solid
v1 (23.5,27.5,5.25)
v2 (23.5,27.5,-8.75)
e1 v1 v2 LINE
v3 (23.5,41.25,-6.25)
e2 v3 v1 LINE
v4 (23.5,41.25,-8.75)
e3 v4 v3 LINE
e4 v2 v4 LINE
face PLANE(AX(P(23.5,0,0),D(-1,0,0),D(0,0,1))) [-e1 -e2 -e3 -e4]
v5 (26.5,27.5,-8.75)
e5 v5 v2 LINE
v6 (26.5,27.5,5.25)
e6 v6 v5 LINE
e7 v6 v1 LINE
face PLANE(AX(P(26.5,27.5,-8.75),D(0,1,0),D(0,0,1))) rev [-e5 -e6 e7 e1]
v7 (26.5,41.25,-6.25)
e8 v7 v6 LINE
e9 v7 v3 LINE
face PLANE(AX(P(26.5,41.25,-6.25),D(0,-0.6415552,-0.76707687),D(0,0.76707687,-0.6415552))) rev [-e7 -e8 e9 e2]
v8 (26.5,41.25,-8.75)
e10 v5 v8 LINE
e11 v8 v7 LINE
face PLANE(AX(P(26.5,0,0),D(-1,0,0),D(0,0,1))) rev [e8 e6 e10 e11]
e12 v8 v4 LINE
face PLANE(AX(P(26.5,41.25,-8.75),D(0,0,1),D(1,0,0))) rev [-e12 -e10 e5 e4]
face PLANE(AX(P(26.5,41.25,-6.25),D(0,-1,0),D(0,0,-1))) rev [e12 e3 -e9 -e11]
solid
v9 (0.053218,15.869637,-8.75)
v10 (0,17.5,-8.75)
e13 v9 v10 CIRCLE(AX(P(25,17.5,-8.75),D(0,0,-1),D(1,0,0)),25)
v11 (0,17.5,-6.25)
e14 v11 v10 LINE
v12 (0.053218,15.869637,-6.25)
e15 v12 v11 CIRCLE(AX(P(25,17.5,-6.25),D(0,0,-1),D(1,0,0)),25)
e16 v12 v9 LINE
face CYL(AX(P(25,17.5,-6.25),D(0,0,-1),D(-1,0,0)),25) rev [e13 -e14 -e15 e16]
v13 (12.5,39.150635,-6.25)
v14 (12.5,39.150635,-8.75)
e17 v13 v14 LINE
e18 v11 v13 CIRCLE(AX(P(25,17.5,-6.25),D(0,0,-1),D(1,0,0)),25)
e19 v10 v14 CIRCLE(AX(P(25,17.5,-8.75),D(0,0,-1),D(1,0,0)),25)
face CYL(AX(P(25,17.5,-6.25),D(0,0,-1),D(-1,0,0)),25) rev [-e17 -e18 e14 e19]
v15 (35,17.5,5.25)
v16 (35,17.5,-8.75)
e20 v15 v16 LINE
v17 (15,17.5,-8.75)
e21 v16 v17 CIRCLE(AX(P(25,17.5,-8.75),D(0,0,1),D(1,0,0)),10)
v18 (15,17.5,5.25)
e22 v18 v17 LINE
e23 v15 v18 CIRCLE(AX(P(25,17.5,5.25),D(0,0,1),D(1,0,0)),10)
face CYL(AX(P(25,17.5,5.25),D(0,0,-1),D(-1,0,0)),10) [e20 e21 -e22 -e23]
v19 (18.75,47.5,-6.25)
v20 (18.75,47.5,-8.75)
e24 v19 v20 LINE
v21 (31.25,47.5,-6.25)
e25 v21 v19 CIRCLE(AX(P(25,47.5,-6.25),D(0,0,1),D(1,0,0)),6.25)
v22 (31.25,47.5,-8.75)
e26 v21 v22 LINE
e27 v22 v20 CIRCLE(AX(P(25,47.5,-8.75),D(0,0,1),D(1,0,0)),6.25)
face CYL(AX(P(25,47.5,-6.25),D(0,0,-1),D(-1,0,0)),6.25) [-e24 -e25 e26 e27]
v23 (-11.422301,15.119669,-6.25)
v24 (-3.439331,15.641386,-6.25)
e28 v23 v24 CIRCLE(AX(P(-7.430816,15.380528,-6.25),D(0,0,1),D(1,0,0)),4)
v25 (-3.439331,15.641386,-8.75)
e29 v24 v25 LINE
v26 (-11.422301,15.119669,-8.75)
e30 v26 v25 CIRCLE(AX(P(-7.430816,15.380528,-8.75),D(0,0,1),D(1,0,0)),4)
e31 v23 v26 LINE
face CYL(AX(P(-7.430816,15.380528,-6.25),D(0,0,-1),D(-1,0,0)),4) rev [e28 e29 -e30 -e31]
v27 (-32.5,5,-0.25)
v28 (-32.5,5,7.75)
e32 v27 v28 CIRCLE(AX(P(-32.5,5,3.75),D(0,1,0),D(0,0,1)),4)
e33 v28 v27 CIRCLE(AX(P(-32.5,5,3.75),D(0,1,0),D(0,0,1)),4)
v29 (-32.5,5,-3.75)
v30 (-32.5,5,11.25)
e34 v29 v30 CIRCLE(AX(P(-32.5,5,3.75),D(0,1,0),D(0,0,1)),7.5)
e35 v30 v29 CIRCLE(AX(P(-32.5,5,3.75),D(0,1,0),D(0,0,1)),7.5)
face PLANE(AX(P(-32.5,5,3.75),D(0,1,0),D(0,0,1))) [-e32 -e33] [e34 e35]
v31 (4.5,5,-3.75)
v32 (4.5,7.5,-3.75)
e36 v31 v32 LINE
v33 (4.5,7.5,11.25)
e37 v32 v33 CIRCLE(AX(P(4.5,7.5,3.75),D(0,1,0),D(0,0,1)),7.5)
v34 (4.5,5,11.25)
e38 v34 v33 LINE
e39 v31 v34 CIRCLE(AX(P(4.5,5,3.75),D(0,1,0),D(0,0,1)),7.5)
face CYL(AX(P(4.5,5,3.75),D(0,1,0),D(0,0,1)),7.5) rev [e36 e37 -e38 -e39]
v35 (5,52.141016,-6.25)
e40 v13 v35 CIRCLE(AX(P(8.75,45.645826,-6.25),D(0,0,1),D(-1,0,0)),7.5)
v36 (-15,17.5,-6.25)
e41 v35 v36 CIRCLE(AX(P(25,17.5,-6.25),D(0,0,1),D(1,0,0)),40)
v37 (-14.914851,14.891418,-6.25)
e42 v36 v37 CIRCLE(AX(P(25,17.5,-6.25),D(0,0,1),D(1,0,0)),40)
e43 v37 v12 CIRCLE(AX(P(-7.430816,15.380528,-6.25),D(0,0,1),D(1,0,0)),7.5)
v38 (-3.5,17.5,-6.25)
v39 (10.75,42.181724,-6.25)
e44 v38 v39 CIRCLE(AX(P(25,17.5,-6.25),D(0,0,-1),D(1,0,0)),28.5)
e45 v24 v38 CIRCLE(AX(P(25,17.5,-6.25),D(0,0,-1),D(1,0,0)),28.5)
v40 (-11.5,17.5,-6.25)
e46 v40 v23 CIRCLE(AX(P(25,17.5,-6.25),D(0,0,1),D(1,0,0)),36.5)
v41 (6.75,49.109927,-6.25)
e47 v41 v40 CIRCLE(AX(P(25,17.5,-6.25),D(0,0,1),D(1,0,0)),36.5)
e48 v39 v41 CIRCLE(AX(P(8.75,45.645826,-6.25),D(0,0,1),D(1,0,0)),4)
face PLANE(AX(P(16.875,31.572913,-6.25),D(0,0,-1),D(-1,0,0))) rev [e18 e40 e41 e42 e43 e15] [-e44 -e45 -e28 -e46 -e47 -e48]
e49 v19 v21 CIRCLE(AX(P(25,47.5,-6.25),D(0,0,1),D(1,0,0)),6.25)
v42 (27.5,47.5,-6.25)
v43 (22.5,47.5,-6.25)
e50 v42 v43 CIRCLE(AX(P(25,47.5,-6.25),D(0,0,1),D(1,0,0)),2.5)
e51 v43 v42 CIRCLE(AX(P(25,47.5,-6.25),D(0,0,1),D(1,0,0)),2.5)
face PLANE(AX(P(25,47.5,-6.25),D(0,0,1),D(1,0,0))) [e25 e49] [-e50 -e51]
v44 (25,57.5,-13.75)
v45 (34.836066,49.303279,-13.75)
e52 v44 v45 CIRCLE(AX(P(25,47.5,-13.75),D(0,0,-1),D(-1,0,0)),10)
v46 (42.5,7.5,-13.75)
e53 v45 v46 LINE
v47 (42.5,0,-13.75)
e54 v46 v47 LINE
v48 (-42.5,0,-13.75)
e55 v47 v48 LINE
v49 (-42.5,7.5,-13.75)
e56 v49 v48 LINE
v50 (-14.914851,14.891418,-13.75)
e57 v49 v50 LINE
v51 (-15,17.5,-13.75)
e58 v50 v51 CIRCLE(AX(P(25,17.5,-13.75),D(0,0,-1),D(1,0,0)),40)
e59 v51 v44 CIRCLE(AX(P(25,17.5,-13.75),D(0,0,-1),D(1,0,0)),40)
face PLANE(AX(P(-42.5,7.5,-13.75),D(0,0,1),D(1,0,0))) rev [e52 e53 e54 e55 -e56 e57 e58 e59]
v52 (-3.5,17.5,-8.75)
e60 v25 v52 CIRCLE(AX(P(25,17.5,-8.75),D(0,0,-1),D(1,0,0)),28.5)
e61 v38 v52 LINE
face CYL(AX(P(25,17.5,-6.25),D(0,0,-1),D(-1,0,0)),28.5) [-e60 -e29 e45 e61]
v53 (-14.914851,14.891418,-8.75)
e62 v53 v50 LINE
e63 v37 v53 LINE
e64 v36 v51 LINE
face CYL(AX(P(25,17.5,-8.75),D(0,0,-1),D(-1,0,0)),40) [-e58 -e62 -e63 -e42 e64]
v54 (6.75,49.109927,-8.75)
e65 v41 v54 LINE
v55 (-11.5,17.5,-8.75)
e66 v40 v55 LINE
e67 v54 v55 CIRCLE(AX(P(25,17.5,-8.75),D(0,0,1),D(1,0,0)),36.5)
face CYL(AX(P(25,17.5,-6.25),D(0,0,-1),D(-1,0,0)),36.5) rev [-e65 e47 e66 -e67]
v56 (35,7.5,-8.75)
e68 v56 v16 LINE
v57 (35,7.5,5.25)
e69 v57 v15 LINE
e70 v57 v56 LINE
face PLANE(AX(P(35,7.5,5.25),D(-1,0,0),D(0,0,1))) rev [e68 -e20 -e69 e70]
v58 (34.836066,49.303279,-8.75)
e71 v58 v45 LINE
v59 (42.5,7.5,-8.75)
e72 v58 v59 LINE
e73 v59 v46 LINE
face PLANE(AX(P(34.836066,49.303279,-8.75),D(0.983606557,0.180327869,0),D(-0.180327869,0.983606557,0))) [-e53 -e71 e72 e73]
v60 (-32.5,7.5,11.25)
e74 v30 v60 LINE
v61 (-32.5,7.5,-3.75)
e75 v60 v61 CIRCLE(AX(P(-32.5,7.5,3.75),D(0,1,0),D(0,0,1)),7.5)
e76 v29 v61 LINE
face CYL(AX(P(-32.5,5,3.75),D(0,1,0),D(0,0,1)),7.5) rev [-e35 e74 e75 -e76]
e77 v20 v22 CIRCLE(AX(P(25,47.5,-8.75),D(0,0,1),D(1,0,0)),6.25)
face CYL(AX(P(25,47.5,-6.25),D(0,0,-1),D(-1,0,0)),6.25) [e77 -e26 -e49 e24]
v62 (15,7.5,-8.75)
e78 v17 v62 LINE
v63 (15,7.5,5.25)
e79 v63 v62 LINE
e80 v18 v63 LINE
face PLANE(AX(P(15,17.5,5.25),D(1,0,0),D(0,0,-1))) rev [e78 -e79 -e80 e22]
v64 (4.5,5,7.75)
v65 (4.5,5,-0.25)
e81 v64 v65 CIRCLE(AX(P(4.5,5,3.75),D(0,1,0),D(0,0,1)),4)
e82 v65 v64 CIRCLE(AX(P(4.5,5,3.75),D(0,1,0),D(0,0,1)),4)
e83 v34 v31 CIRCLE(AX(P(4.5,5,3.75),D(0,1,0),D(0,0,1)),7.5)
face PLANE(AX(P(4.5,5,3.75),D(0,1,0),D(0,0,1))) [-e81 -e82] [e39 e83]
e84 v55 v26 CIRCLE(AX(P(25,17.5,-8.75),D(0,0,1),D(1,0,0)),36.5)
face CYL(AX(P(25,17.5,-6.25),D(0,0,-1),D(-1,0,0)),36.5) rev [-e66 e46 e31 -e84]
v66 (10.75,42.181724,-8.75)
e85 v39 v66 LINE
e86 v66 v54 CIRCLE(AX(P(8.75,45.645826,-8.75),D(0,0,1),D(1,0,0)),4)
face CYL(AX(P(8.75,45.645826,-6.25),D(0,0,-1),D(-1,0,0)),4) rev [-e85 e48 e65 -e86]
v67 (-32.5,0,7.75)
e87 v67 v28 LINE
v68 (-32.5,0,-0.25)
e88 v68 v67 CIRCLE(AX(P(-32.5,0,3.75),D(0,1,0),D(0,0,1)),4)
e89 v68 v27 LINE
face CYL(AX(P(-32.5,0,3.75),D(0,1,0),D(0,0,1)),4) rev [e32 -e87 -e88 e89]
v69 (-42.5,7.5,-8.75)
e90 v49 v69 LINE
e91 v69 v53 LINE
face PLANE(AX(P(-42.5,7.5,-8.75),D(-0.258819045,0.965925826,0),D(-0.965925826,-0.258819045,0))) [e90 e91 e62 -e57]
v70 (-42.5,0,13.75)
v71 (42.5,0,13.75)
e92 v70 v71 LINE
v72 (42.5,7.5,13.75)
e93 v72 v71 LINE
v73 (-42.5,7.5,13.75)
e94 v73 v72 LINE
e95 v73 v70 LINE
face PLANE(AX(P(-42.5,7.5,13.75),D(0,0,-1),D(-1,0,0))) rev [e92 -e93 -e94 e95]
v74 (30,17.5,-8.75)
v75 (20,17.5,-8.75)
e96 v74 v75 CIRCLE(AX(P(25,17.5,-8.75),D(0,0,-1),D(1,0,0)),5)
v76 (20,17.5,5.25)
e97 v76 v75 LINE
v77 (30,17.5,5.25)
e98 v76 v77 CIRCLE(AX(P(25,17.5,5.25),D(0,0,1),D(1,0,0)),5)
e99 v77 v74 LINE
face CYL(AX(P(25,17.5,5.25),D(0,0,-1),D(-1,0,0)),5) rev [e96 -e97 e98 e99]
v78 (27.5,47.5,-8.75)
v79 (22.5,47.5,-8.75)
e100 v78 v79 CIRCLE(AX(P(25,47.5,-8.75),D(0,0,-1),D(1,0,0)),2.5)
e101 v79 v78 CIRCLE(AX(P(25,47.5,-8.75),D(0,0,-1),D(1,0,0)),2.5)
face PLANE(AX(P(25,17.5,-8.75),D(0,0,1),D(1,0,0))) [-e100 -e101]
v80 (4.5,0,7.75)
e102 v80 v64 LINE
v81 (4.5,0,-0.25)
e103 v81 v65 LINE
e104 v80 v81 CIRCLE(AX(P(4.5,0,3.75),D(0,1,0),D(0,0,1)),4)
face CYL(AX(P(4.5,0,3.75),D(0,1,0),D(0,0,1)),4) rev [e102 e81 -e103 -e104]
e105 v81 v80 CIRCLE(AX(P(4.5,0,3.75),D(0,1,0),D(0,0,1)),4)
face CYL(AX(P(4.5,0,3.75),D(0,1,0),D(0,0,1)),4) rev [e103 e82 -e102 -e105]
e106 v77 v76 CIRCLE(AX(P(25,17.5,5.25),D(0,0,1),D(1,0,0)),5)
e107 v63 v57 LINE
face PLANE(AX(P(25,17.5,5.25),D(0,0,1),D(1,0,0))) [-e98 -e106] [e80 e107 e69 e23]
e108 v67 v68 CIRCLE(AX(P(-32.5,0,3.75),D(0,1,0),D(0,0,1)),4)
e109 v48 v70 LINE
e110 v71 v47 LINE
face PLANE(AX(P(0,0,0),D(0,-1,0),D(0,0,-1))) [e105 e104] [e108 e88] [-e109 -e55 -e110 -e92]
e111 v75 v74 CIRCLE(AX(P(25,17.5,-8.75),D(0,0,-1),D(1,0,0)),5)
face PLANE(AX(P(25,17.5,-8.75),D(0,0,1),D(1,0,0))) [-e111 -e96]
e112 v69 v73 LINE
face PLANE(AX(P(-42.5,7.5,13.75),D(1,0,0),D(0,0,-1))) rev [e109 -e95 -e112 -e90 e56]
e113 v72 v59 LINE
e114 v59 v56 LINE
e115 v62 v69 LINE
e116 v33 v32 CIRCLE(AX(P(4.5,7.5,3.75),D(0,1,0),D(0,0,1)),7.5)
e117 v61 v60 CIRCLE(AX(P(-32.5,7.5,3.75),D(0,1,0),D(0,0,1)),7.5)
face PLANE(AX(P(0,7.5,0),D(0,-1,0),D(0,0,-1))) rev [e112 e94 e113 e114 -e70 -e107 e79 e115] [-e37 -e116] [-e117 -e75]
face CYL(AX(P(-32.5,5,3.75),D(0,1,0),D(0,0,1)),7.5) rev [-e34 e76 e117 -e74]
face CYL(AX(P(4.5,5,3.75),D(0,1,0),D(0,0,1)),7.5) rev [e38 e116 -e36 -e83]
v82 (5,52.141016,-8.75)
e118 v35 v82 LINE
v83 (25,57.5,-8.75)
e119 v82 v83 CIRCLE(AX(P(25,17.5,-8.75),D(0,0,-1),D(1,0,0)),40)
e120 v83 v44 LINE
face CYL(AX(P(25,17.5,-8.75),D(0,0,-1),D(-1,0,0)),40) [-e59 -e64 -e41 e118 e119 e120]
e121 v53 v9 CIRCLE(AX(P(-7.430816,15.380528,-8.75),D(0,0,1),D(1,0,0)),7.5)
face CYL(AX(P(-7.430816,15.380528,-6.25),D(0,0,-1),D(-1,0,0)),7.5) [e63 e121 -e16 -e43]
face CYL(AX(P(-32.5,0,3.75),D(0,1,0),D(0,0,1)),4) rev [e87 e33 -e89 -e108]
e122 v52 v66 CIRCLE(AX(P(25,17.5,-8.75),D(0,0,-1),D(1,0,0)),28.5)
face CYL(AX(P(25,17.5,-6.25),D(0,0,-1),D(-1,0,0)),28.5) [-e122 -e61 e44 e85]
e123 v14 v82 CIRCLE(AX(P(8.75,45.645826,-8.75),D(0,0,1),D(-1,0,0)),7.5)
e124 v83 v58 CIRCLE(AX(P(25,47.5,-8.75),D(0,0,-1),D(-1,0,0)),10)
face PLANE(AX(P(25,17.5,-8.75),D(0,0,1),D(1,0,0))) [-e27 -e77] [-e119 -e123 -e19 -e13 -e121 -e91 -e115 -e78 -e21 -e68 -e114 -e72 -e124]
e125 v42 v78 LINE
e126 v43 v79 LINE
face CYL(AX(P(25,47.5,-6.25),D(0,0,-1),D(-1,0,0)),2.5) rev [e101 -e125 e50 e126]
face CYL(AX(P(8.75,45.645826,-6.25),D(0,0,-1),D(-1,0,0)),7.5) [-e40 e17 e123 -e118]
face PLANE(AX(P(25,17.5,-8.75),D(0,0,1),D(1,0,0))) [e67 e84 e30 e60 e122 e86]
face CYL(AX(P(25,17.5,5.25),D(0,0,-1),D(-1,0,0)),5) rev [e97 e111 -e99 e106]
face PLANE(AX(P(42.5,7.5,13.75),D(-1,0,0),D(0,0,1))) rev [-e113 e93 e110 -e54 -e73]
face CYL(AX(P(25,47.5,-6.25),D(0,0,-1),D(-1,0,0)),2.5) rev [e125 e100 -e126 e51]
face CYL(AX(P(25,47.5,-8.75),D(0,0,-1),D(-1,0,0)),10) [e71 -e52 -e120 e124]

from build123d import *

# Parameters (mm, degrees)
BASE_PLATE_SKETCH_W         = 85
BASE_PLATE_SKETCH_H         = 27.5
BASE_PLATE_DEPTH            = 7.5
UPRIGHT_DEPTH               = 5
UPRIGHT_RIM_BOSS_SKETCH_R   = 6.25
UPRIGHT_RIM_BOSS_SKETCH_R_2 = 2.5
UPRIGHT_RIM_BOSS_DEPTH      = 2.5
BUSHING_BLOCK_SKETCH_R      = 5
BUSHING_BLOCK_DEPTH         = 14
COUNTERBORE_SKETCH_2X_15_R  = 7.5
COUNTERBORES_2X_15_DEPTH    = 2.5
MOUNTING_HOLE_SKETCH_2X_8_R = 4
MOUNTING_HOLES_2X_8_DEPTH   = 69.931578395
LINK_PLATE_DEPTH            = 1.5
CURVED_GUIDE_RIB_DEPTH      = 2.5


with BuildPart() as part:
    # Base Plate Sketch → Base Plate (new body)
    with BuildSketch(Plane(origin=(0, 0, 0), x_dir=(1, 0, 0), z_dir=(0, 1, 0))):
        Rectangle(BASE_PLATE_SKETCH_W, BASE_PLATE_SKETCH_H)
    extrude(amount=BASE_PLATE_DEPTH)

    # Upright Profile Sketch → Upright (add)
    with BuildSketch(Plane(origin=(0, 0, -13.75), x_dir=(-1, 0, 0), z_dir=(0, 0, -1))):
        with BuildLine():
            Line((42.5, 7.5), (14.914850651, 14.891418491))
            ThreePointArc((14.914850651, 14.891418491), (4.191978867, 44.846450772), (-25, 57.5))
            ThreePointArc((-25, 57.5), (-31.401843997, 55.182212796), (-34.836065574, 49.303278689))
            Line((-34.836065574, 49.303278689), (-42.5, 7.5))
            Line((-42.5, 7.5), (42.5, 7.5))
        make_face()
    extrude(amount=-UPRIGHT_DEPTH)

    # Upright Rim Boss Sketch → Upright Rim Boss (add)
    with BuildSketch(Plane.XY.offset(-8.75)):
        with Locations((25, 47.5)):
            Circle(UPRIGHT_RIM_BOSS_SKETCH_R)
        with Locations((25, 47.5)):
            Circle(UPRIGHT_RIM_BOSS_SKETCH_R_2, mode=Mode.SUBTRACT)
    extrude(amount=UPRIGHT_RIM_BOSS_DEPTH)

    # Bushing Block Sketch → Bushing Block (add)
    with BuildSketch(Plane.XY.offset(-8.75)):
        with BuildLine():
            Line((15, 17.5), (15, 7.5))
            Line((15, 7.5), (35, 7.5))
            Line((35, 7.5), (35, 17.5))
            ThreePointArc((35, 17.5), (25, 27.5), (15, 17.5))
        make_face()
        with Locations((25, 17.5)):
            Circle(BUSHING_BLOCK_SKETCH_R, mode=Mode.SUBTRACT)
    extrude(amount=BUSHING_BLOCK_DEPTH)

    # Counterbore Sketch 2xØ15 → Counterbores 2xØ15 (cut)
    with BuildSketch(Plane(origin=(0, 7.5, 0), x_dir=(1, 0, 0), z_dir=(0, 1, 0))):
        with Locations(Location((4.5, -3.75, 0), (0, 0, 270))):
            Circle(COUNTERBORE_SKETCH_2X_15_R)
        with Locations(Location((-32.5, -3.75, 0), (0, 0, 270))):
            Circle(COUNTERBORE_SKETCH_2X_15_R)
    extrude(amount=-COUNTERBORES_2X_15_DEPTH, mode=Mode.SUBTRACT)

    # Mounting Hole Sketch 2xØ8 → Mounting Holes 2xØ8 (cut, through all)
    with BuildSketch(Plane(origin=(0, 5, 0), x_dir=(1, 0, 0), z_dir=(0, 1, 0))):
        with Locations(Location((-32.5, -3.75, 0), (0, 0, 270))):
            Circle(MOUNTING_HOLE_SKETCH_2X_8_R)
        with Locations(Location((4.5, -3.75, 0), (0, 0, 270))):
            Circle(MOUNTING_HOLE_SKETCH_2X_8_R)
    extrude(amount=-MOUNTING_HOLES_2X_8_DEPTH, mode=Mode.SUBTRACT)

    # Curved Guide Rib Sketch → Curved Guide Rib (add)
    with BuildSketch(Plane.XY.offset(-8.75)):
        with BuildLine():
            ThreePointArc((5, 52.141016151), (-10.275068584, 36.359202963), (-14.914850651, 14.891418491))
            ThreePointArc((-14.914850651, 14.891418491), (-6.941707121, 7.896493027), (0.053218343, 15.869636557))
            ThreePointArc((0.053218343, 15.869636557), (2.953082135, 29.287001852), (12.5, 39.150635095))
            ThreePointArc((12.5, 39.150635095), (15.245190528, 49.395825623), (5, 52.141016151))
        make_face()
        with BuildLine():
            ThreePointArc((6.75, 49.109927238), (-7.188500083, 34.709022704), (-11.422301219, 15.119669373))
            ThreePointArc((-11.422301219, 15.119669373), (-7.169958003, 11.389042459), (-3.439331089, 15.641385675))
            ThreePointArc((-3.439331089, 15.641385675), (-0.133486366, 30.937182111), (10.75, 42.181724008))
            ThreePointArc((10.75, 42.181724008), (12.214101615, 47.645825623), (6.75, 49.109927238))
        make_face(mode=Mode.SUBTRACT)
    extrude(amount=CURVED_GUIDE_RIB_DEPTH)


with BuildPart() as body_2:
    # Link Plate Sketch → Link Plate (new, symmetric)
    with BuildSketch(Plane(origin=(25, 0, 0), x_dir=(0, 0, -1), z_dir=(1, 0, 0))):
        Polygon((6.25, 41.25), (-5.25, 27.5), (8.75, 27.5), (8.75, 41.25), align=None)
    extrude(amount=LINK_PLATE_DEPTH, both=True)


solid = Compound([part.part, body_2.part])
